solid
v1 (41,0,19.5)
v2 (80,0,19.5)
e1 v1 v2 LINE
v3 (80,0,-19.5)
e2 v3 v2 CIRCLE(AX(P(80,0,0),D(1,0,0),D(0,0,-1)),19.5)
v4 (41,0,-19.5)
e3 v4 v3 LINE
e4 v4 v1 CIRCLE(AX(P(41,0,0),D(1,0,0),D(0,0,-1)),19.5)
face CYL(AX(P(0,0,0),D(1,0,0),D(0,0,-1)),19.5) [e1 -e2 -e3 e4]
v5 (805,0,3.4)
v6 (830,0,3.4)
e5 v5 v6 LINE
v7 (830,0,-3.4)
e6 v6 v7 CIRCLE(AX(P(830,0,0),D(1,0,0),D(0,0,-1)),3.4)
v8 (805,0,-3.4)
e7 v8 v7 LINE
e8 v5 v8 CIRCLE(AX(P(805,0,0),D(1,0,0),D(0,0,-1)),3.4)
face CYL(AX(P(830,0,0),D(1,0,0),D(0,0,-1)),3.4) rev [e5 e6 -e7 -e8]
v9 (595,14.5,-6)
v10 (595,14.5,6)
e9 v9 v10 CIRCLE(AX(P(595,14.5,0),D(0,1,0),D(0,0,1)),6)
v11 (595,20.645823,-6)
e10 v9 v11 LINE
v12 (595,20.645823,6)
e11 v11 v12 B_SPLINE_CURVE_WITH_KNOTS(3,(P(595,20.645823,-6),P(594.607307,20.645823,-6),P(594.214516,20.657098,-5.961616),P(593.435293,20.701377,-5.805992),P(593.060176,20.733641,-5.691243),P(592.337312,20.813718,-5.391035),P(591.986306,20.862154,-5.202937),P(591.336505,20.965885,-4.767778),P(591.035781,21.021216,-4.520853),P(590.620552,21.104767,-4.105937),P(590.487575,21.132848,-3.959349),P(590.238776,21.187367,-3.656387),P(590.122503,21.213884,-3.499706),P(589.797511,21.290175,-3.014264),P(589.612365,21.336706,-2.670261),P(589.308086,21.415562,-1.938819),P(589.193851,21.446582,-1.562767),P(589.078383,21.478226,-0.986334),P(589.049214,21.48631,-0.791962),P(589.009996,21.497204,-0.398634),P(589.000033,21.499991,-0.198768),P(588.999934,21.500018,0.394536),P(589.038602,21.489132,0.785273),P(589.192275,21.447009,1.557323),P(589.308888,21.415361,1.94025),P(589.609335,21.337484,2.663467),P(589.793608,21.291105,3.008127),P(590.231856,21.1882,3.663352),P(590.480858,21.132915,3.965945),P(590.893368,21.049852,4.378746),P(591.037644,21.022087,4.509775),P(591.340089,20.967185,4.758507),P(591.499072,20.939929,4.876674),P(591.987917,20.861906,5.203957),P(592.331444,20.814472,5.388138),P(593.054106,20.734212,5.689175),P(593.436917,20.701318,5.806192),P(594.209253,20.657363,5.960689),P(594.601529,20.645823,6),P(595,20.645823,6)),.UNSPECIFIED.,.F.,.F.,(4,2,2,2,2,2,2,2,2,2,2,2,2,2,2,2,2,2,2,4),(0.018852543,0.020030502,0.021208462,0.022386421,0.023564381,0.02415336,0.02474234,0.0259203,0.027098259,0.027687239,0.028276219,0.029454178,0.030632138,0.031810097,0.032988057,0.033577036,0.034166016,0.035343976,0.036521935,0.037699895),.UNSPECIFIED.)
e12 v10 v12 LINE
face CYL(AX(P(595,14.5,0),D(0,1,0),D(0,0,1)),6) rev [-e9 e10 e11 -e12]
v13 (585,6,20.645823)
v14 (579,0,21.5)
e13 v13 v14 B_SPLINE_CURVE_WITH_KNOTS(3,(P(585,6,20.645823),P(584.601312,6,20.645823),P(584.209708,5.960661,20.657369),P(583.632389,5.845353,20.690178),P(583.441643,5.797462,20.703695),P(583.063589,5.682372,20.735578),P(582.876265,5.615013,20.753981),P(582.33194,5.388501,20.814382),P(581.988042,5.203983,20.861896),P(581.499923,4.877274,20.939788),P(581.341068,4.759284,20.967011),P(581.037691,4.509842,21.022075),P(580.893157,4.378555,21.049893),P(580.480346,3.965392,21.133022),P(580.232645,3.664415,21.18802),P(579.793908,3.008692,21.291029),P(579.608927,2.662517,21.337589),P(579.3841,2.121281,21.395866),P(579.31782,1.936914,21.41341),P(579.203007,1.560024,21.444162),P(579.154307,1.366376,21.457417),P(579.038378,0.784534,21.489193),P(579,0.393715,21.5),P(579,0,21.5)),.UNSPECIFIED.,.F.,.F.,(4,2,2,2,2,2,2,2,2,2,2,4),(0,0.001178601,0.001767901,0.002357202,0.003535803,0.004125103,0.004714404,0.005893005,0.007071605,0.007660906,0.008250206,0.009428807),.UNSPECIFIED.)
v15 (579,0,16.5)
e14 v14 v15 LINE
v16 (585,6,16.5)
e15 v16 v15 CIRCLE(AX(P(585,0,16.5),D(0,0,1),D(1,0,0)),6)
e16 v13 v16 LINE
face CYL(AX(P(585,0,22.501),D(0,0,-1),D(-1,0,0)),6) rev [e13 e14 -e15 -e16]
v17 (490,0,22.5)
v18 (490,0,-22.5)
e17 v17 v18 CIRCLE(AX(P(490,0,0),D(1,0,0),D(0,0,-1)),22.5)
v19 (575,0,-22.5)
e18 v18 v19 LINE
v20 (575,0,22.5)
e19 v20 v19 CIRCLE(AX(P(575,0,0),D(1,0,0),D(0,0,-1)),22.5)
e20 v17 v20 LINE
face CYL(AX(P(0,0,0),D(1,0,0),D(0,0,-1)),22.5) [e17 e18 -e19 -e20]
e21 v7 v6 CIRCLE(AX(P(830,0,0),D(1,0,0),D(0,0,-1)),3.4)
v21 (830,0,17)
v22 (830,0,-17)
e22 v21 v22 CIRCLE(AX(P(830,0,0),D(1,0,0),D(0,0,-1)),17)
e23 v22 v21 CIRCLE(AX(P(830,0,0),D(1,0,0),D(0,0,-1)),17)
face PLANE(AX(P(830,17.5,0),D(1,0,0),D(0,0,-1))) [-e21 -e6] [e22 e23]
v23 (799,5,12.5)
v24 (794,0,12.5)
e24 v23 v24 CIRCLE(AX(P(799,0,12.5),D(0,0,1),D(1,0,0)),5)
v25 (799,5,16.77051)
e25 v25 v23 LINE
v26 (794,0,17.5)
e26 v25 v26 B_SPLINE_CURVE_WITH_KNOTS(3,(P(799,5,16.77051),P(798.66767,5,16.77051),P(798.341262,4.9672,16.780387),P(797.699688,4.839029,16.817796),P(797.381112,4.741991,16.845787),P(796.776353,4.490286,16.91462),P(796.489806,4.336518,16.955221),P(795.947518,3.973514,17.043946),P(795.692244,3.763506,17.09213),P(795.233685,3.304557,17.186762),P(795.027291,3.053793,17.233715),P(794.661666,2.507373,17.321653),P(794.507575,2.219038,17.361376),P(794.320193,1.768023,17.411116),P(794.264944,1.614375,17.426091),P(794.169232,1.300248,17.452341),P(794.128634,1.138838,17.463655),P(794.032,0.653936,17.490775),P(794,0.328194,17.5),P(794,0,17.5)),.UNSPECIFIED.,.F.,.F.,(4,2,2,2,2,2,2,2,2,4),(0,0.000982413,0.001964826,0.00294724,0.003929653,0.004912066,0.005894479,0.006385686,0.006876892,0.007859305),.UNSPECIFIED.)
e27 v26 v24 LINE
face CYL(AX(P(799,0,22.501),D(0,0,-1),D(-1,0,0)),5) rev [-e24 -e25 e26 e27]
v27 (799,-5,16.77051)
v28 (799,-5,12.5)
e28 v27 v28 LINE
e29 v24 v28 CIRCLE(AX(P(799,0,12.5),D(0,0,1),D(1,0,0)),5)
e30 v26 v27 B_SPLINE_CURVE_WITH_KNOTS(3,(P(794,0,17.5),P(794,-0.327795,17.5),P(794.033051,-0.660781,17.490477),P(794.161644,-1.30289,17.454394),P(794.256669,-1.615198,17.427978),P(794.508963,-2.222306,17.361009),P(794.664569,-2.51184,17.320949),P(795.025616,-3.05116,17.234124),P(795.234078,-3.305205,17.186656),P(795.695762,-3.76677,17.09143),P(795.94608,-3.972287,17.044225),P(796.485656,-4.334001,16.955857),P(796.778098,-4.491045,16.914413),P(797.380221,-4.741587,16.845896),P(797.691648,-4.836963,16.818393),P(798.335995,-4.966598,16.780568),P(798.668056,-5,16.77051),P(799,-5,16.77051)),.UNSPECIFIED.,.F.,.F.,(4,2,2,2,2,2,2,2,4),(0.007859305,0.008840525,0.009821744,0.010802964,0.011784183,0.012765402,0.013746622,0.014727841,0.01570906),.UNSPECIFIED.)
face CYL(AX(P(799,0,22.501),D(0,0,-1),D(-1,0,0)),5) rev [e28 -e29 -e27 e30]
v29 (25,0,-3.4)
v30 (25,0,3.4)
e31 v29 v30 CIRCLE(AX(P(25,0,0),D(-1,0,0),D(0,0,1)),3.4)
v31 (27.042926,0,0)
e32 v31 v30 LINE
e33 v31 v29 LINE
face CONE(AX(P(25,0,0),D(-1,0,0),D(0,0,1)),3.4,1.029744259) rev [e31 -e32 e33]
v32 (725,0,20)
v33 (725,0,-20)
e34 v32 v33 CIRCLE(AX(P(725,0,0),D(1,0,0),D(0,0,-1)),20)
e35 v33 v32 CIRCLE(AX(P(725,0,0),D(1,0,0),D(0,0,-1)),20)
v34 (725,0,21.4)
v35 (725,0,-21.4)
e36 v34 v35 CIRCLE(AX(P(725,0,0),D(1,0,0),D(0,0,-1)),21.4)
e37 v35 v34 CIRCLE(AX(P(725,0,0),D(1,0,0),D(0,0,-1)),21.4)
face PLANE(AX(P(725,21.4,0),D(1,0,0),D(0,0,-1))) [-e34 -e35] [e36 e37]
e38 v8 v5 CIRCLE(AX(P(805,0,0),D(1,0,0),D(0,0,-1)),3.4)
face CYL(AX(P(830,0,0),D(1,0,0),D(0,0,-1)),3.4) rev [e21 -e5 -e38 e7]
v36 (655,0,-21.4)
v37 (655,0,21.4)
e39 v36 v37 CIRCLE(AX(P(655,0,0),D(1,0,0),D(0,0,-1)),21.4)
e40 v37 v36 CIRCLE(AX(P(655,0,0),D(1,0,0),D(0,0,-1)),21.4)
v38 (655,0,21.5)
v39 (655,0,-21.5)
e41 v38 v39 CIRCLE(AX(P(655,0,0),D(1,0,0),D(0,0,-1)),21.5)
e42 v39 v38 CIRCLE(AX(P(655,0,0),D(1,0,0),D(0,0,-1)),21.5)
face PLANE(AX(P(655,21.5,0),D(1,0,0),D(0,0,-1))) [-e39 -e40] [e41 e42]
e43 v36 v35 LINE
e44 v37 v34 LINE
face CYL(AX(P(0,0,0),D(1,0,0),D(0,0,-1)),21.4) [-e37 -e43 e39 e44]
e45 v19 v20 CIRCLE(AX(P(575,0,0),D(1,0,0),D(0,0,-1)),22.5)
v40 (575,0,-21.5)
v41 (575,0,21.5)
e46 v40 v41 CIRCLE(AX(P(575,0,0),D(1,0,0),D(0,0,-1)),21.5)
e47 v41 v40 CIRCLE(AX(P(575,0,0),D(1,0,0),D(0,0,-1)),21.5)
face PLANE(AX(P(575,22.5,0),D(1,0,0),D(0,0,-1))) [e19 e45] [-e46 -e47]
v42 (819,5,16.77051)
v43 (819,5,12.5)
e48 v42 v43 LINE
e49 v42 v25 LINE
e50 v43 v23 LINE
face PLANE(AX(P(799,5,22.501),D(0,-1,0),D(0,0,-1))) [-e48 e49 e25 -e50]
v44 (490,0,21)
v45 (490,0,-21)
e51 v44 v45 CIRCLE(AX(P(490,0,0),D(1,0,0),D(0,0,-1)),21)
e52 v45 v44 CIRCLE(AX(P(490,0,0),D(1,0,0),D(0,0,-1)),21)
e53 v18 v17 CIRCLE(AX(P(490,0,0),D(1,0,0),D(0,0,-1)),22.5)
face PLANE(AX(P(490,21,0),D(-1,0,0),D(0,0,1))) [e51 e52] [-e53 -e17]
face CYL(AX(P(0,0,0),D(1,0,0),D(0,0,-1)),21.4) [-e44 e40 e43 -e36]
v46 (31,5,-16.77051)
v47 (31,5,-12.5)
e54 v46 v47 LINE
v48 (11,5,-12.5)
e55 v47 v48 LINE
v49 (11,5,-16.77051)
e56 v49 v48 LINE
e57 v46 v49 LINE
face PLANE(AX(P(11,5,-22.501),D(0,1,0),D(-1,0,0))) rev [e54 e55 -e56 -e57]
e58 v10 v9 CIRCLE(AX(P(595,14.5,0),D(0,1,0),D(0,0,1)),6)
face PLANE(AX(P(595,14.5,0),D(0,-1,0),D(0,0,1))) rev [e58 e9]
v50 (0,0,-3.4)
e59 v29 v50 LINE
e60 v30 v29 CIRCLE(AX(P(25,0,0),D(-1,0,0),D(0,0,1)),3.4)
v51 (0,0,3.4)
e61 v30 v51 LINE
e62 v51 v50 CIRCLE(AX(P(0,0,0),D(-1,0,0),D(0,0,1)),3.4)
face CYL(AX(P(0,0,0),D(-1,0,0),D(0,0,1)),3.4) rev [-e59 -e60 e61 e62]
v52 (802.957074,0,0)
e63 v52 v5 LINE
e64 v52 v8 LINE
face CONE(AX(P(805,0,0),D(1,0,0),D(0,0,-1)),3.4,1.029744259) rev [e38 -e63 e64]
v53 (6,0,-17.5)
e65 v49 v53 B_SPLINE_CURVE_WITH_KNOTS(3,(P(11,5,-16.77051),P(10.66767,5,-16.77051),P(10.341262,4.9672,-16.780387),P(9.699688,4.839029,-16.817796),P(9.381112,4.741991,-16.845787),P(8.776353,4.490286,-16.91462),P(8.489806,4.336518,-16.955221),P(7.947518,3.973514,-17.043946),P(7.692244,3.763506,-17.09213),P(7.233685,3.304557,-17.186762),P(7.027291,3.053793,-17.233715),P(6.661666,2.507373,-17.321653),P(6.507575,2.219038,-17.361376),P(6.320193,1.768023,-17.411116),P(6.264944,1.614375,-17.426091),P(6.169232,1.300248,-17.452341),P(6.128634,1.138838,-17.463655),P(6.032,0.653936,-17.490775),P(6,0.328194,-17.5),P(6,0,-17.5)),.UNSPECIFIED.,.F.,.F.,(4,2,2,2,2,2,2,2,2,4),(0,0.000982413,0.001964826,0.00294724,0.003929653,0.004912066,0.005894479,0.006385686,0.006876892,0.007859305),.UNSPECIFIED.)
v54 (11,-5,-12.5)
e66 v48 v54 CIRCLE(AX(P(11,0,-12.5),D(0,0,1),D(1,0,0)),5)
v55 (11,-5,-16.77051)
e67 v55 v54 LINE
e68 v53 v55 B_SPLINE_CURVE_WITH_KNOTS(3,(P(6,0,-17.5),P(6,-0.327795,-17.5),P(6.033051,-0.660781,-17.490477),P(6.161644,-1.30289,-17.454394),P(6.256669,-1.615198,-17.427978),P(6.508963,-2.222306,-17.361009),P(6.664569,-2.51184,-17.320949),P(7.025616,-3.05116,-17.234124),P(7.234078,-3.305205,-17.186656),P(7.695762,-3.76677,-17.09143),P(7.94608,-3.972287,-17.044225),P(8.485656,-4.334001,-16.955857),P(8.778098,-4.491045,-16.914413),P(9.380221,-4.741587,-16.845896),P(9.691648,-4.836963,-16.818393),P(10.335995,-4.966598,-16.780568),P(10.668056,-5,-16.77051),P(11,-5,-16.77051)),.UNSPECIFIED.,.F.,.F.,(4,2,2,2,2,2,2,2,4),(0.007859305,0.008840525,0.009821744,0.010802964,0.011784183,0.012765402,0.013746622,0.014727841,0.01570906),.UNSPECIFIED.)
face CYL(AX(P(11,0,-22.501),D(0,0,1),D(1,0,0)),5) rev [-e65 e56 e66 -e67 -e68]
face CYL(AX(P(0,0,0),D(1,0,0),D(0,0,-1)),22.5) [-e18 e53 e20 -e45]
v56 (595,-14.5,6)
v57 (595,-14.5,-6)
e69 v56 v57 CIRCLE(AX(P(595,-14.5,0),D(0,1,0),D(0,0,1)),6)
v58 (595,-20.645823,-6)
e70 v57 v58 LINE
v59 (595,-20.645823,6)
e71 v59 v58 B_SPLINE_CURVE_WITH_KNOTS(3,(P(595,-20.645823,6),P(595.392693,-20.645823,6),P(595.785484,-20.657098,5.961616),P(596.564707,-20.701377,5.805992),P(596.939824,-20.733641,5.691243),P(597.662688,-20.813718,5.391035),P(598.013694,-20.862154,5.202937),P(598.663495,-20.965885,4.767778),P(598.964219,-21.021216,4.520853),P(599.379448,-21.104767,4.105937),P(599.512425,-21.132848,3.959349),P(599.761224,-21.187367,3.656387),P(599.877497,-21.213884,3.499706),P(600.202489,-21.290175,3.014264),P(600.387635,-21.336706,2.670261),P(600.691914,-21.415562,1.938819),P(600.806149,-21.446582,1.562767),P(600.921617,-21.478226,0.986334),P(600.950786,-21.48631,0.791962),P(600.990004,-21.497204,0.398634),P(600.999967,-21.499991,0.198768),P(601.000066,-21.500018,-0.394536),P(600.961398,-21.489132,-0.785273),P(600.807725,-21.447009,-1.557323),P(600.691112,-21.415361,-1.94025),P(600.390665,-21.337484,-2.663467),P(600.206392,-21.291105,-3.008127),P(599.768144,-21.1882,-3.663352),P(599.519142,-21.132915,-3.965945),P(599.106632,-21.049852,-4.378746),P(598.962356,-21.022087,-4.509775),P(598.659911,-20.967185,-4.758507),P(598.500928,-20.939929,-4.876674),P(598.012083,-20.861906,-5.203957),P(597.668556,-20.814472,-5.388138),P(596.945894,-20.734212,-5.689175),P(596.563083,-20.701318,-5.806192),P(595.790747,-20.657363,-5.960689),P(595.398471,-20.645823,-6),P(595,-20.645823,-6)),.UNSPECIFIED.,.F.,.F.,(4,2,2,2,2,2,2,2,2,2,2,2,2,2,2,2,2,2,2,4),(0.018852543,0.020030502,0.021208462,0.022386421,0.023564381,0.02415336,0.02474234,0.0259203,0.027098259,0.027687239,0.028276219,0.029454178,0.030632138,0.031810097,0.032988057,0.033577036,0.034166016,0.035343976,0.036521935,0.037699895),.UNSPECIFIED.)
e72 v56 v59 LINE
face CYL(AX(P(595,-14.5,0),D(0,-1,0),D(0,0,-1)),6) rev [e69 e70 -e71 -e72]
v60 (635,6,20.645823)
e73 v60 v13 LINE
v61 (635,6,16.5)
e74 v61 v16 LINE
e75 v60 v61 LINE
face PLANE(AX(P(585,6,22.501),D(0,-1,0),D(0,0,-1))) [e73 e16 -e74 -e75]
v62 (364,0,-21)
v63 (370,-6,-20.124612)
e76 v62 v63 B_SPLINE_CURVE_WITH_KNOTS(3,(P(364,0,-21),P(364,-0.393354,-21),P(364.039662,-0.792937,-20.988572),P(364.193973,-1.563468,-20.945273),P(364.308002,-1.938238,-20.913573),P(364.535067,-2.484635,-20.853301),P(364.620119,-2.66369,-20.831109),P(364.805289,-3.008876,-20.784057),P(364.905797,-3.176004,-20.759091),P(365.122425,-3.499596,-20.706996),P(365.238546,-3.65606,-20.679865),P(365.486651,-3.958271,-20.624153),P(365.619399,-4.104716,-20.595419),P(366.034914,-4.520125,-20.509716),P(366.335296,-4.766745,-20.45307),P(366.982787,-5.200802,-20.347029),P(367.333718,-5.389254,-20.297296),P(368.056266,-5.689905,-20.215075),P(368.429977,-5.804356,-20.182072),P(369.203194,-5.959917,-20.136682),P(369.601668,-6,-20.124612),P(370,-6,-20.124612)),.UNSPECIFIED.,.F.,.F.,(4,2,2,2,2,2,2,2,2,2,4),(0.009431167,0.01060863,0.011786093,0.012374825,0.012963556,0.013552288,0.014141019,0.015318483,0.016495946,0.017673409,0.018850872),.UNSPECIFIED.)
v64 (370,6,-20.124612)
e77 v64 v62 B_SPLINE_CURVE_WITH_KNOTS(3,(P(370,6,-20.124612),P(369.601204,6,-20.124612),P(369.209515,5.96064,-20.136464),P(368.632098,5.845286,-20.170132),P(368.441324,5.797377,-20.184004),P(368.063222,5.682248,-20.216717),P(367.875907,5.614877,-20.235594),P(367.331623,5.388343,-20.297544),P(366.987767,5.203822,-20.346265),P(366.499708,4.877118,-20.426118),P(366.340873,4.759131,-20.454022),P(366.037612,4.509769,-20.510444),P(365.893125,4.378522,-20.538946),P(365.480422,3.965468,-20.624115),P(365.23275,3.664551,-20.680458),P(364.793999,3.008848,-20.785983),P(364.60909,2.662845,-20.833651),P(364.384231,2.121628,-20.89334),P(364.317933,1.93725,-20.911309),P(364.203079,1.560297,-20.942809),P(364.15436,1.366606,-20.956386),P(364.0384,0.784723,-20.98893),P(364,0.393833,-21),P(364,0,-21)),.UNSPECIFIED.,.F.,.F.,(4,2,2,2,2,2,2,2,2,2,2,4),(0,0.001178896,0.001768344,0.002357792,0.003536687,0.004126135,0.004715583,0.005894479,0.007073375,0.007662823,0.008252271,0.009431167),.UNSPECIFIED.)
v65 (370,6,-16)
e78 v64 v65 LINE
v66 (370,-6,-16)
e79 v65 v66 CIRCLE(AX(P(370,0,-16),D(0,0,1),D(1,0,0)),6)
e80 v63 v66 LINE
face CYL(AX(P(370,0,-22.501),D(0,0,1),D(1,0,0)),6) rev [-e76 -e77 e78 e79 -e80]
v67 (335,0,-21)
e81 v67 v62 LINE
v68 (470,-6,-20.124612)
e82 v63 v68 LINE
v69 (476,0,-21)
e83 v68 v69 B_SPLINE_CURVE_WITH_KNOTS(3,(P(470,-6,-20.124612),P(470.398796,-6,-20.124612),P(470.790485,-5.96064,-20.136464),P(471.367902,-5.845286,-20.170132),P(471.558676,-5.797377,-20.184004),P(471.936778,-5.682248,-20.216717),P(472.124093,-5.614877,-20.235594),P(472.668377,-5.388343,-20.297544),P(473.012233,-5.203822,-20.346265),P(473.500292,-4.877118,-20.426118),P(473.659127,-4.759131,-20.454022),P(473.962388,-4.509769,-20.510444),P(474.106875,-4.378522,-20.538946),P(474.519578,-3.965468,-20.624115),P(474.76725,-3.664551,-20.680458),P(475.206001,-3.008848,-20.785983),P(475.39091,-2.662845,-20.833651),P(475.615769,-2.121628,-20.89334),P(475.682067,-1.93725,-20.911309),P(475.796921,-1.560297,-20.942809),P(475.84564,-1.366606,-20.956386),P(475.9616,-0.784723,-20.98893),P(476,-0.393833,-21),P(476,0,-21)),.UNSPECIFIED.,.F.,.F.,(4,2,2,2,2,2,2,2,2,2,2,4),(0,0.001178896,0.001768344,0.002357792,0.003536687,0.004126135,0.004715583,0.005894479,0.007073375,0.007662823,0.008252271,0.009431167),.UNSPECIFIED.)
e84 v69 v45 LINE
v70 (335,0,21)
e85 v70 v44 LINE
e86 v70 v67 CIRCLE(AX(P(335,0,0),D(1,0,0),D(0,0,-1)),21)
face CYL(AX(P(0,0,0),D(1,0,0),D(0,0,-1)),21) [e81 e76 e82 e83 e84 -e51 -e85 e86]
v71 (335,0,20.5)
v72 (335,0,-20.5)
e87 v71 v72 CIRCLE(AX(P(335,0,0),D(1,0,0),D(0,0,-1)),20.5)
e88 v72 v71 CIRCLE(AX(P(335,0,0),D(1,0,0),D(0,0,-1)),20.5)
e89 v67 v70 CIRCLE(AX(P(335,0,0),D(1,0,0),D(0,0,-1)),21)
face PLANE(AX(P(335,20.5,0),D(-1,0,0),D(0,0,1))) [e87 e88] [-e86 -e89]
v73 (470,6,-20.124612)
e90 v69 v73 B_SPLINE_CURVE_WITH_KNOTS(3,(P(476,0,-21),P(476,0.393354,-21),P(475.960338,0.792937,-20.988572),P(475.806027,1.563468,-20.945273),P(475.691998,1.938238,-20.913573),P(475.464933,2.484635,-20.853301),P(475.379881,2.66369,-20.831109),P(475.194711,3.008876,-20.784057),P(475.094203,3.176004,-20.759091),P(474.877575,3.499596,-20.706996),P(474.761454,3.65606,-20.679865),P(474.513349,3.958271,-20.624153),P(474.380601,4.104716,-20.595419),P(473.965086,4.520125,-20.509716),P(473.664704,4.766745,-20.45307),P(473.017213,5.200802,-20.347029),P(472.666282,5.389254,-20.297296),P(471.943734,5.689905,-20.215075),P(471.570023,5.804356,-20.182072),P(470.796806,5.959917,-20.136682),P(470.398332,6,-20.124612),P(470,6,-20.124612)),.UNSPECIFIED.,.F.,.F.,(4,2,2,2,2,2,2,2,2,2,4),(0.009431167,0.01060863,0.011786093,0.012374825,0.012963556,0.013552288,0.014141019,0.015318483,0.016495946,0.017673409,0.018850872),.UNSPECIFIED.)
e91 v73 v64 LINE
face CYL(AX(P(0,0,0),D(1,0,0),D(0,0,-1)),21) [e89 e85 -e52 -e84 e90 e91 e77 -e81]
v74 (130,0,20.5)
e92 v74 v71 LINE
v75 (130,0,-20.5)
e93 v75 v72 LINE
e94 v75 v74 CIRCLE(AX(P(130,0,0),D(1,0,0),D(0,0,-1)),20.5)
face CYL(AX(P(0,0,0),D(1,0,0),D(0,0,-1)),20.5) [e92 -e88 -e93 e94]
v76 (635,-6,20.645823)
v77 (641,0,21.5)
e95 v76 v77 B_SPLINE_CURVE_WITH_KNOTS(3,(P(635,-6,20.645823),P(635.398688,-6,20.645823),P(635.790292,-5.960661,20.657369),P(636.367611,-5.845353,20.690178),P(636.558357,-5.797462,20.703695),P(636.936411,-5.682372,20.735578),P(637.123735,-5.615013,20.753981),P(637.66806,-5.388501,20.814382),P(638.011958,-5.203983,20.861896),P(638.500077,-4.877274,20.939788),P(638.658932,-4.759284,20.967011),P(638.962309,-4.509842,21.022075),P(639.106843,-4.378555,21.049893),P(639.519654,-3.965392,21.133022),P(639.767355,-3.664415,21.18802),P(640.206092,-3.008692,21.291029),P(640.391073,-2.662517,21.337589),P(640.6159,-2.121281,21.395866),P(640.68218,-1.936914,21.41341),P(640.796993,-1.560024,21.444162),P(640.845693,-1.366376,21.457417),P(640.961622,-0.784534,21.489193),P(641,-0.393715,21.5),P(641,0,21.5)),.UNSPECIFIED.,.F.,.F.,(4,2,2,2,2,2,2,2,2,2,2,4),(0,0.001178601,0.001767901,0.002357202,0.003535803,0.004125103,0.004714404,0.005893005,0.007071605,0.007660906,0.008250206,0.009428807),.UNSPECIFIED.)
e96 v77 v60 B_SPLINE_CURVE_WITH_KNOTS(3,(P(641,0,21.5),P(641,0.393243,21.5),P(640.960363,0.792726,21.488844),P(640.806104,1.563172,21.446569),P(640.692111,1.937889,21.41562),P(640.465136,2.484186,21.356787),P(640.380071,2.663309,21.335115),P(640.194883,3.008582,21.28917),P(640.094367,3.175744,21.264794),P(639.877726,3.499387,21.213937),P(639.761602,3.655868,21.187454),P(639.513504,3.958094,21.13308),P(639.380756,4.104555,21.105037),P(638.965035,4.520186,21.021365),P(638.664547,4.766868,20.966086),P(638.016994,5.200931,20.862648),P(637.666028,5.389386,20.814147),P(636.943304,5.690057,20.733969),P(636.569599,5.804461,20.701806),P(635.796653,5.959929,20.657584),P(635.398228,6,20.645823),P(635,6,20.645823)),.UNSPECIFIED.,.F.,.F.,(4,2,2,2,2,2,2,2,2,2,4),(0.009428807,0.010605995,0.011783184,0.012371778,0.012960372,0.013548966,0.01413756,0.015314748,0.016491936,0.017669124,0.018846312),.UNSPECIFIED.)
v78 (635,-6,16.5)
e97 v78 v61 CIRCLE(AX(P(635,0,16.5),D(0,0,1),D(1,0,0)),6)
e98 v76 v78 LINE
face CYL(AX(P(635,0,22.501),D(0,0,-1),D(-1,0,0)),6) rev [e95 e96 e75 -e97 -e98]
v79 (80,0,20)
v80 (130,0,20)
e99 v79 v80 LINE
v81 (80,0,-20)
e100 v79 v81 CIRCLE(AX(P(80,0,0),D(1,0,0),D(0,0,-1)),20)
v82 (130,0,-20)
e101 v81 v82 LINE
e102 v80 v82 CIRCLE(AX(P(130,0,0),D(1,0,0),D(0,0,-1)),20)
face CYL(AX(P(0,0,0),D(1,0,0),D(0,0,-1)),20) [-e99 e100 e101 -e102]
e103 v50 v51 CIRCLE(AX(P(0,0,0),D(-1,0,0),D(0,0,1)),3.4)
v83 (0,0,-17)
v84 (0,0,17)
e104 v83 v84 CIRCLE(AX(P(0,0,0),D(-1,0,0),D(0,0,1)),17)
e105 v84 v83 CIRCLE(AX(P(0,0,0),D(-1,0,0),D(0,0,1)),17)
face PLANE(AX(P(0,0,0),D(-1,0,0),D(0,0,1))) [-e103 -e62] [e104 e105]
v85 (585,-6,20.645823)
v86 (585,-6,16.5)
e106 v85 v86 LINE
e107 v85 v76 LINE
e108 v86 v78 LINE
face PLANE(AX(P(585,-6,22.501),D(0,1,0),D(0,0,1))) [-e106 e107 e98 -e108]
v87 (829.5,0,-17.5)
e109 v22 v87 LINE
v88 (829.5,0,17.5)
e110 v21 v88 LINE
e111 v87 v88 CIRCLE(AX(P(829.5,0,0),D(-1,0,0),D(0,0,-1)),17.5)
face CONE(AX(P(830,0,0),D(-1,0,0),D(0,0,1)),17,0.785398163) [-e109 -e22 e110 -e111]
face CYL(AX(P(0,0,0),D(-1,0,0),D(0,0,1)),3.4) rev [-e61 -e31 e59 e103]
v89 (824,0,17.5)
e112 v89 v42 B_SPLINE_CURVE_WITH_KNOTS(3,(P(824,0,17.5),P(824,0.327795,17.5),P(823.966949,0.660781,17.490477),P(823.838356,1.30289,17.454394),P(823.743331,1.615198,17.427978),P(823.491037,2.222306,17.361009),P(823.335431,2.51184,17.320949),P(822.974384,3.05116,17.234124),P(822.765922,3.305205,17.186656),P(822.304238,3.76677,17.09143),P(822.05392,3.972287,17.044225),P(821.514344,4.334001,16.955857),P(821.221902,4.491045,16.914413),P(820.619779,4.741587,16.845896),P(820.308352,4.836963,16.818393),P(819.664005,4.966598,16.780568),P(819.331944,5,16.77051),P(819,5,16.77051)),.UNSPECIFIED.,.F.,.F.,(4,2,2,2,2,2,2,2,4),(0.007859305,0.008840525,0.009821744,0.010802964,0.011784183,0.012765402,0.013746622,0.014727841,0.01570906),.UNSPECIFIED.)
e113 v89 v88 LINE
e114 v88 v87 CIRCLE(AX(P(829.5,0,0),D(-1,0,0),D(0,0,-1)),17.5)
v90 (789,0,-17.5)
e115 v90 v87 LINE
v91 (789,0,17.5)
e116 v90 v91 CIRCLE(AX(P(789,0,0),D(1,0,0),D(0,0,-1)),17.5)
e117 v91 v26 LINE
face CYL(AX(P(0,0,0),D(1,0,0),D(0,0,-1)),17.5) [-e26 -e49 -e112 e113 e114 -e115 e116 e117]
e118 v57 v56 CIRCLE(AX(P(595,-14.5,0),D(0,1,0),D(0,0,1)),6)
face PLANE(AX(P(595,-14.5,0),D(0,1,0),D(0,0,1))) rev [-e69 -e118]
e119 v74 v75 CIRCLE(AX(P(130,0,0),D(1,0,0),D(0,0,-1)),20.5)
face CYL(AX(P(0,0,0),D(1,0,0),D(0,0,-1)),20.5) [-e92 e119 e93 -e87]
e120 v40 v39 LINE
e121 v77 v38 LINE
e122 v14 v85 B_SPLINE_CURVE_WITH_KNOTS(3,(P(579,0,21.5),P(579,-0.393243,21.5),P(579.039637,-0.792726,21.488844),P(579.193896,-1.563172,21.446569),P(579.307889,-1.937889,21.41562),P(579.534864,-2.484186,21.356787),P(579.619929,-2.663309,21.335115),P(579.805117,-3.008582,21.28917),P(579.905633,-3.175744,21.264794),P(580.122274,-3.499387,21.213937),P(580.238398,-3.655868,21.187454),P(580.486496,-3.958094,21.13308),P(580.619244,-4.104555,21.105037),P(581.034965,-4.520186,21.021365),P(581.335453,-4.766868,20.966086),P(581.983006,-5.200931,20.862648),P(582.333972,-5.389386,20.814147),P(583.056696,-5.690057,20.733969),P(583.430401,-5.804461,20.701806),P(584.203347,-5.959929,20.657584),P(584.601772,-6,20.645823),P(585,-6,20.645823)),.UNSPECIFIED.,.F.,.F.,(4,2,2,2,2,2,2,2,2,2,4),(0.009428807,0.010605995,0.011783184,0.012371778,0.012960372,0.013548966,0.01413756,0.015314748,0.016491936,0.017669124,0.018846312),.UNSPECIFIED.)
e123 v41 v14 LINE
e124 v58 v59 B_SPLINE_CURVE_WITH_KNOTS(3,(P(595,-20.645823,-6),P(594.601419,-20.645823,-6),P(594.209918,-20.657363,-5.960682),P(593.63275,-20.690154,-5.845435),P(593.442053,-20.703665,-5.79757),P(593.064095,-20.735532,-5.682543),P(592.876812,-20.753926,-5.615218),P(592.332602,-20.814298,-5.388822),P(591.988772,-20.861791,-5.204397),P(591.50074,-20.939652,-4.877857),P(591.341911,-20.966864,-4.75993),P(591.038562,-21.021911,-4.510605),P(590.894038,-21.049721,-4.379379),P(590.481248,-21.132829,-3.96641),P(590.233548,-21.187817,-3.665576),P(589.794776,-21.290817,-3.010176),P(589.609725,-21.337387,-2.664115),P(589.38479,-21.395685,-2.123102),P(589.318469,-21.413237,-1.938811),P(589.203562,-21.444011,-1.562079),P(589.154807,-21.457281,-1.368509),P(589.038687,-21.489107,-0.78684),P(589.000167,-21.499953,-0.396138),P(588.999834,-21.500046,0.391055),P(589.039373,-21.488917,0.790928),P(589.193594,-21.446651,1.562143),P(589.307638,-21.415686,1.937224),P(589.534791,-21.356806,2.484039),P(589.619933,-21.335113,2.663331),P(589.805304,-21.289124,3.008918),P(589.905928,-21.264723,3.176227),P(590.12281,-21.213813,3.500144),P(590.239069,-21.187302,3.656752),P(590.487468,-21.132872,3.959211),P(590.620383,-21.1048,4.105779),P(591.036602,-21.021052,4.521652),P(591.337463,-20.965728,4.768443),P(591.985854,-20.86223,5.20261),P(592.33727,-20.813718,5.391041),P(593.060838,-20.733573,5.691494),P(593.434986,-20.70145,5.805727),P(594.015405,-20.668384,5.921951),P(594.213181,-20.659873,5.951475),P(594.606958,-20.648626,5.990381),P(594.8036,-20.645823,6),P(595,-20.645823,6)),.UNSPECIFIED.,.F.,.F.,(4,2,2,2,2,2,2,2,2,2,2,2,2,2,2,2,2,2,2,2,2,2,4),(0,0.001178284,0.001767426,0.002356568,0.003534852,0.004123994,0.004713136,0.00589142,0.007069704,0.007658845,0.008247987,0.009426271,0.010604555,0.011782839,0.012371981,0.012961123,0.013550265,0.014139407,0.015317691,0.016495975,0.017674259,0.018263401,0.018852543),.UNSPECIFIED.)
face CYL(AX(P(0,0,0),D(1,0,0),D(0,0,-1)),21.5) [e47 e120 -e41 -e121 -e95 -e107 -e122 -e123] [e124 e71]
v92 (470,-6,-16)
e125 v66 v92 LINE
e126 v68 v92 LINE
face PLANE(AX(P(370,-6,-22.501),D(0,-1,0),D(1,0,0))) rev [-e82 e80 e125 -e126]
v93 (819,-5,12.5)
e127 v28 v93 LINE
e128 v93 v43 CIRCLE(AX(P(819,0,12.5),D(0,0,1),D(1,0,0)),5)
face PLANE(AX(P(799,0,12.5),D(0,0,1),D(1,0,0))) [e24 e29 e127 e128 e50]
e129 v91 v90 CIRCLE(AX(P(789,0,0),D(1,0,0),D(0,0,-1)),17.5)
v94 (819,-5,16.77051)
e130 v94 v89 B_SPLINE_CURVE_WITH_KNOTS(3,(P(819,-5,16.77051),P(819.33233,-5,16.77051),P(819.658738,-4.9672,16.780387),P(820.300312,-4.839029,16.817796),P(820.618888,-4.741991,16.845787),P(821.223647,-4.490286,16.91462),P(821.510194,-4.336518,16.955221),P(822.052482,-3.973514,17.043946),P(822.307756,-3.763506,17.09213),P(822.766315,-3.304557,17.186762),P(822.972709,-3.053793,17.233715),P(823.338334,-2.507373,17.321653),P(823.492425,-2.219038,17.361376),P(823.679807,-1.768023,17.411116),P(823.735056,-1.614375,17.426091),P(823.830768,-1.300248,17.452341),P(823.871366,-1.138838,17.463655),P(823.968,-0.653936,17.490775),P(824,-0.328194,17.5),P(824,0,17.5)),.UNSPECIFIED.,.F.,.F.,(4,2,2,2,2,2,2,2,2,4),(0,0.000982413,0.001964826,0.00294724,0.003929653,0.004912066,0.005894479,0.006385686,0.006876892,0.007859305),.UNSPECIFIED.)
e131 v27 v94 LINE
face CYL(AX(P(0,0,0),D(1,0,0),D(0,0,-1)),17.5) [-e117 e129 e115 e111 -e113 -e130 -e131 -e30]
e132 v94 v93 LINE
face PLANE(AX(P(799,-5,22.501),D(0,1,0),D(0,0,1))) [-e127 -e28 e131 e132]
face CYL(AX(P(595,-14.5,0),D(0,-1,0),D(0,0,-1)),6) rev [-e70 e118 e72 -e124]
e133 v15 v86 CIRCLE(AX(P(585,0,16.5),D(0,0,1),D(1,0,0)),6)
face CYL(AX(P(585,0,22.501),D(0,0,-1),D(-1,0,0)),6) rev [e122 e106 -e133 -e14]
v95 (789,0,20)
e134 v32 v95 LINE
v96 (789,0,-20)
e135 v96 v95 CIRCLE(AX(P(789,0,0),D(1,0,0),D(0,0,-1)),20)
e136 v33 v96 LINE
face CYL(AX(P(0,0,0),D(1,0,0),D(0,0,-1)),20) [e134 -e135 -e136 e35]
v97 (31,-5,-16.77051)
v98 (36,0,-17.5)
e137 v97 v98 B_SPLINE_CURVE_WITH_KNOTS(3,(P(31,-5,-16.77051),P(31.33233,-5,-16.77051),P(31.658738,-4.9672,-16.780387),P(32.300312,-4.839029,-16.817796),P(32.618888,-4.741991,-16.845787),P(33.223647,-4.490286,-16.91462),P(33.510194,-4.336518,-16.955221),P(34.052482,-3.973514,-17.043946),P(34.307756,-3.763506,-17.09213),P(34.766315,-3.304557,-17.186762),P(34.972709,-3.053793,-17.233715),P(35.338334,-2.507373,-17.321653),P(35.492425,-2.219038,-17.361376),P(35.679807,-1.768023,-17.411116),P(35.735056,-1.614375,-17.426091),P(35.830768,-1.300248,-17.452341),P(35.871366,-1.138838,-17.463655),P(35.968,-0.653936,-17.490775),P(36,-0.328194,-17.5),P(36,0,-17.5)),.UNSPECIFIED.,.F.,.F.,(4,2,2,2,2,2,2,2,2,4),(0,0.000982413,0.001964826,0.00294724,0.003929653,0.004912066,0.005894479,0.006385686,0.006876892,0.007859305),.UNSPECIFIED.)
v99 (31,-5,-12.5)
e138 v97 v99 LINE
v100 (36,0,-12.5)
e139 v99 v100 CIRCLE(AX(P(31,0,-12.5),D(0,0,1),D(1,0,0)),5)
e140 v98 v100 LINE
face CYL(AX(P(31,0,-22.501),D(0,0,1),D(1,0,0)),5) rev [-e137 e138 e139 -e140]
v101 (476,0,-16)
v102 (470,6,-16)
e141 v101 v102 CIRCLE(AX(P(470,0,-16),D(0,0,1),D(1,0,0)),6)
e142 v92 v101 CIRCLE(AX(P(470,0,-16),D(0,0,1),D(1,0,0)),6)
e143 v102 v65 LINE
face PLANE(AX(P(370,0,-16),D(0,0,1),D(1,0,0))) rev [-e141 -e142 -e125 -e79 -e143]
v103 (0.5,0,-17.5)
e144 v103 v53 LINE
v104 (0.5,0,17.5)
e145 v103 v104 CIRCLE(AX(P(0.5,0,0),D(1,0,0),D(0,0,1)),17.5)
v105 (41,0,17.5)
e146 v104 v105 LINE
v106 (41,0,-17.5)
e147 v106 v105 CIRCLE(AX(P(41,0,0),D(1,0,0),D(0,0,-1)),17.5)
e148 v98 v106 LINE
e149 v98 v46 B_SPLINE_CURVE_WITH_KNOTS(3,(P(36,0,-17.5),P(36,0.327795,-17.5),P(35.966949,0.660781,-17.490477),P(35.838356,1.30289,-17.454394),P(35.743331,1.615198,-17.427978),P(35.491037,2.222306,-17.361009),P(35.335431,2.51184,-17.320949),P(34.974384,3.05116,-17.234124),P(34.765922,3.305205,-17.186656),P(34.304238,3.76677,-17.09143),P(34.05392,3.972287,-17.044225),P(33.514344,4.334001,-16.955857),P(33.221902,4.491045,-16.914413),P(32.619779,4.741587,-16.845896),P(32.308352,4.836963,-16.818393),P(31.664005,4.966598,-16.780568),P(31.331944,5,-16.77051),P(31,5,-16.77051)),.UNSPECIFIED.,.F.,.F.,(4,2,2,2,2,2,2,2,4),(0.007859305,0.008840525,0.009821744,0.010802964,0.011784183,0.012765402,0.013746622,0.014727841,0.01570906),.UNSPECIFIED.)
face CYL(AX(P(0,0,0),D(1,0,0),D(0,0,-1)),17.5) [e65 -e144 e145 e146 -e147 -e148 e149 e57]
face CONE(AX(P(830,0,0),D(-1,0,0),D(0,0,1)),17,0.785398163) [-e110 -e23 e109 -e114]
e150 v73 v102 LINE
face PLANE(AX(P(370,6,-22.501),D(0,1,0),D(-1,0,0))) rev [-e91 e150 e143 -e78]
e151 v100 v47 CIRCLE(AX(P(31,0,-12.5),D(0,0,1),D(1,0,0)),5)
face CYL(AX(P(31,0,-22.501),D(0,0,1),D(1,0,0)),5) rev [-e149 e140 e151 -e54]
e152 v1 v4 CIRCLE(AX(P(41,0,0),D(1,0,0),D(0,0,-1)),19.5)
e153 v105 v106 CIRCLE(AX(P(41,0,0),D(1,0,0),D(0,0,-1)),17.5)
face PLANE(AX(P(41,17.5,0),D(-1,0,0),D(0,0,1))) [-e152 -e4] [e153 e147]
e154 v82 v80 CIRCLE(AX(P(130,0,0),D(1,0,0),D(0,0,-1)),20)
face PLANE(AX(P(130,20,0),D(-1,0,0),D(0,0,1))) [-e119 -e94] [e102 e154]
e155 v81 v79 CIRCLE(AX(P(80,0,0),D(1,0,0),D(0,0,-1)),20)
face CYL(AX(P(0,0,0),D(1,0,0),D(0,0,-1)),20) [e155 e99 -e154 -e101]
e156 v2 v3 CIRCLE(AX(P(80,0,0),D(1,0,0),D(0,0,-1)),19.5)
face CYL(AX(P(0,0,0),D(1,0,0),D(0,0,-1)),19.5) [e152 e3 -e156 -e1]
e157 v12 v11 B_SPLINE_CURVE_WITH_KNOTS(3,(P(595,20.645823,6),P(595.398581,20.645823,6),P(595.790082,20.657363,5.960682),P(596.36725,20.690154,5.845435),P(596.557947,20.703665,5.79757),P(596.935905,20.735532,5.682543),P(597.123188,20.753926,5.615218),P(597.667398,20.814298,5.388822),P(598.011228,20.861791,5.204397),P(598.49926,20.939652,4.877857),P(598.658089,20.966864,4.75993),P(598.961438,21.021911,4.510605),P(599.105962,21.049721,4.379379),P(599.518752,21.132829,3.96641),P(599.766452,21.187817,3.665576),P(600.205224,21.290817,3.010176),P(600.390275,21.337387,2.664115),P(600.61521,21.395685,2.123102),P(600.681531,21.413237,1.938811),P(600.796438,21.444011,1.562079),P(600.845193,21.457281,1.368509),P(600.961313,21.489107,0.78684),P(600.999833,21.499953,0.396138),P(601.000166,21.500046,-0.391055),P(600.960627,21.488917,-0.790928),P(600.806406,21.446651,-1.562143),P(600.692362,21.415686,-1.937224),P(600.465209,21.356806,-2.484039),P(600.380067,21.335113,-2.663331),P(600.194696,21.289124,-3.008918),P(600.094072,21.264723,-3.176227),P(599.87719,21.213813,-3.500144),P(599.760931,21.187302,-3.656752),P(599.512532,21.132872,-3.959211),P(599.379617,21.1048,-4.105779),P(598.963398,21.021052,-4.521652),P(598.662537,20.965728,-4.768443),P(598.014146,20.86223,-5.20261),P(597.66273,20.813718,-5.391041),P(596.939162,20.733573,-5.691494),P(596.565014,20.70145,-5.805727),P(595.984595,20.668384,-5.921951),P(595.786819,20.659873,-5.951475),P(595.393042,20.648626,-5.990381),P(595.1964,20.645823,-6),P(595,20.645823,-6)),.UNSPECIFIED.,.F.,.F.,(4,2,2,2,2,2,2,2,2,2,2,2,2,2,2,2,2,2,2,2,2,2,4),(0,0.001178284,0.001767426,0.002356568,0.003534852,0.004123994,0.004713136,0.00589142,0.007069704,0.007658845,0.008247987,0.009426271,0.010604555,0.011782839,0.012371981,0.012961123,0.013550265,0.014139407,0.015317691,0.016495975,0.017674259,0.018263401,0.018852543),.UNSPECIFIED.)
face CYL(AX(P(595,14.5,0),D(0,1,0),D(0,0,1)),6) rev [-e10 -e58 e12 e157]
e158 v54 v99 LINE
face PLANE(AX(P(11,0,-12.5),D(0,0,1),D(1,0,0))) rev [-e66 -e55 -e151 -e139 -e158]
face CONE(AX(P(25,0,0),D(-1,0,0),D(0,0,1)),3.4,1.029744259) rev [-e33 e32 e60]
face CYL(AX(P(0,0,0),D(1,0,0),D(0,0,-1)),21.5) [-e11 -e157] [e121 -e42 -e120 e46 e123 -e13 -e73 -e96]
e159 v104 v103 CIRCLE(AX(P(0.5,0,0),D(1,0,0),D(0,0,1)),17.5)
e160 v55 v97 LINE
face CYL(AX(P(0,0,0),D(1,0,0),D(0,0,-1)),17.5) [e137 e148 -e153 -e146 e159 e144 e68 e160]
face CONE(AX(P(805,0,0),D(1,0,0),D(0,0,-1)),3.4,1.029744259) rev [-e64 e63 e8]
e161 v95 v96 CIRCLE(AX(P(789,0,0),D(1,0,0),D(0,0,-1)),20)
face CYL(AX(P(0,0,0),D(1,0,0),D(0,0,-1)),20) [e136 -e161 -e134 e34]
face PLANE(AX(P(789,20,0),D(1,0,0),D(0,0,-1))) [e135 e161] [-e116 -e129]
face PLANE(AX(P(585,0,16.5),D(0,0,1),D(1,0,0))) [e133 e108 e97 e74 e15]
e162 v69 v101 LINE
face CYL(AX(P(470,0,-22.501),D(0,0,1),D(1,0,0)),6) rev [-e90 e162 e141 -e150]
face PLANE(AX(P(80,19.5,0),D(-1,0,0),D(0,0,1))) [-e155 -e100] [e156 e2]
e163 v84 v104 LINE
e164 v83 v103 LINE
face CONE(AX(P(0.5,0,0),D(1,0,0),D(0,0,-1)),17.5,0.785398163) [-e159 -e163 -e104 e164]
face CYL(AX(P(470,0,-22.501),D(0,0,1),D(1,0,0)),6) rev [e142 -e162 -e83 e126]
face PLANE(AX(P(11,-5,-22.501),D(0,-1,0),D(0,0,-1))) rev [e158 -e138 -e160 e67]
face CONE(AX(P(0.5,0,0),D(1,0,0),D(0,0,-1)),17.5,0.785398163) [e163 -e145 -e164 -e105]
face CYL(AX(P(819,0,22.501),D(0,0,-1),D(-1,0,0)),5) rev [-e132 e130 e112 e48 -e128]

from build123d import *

# Parameters (mm, degrees)
M8_TAPPED_HOLE1_D       = 6.8
M8_TAPPED_HOLE1_DEPTH   = 25
M8_TAPPED_HOLE1_TIP     = 2.042926105
M8_TAPPED_HOLE2_D       = 6.8
M8_TAPPED_HOLE2_DEPTH   = 25
M8_TAPPED_HOLE2_TIP     = 2.042926105
CUT_EXTRUDE1_REACH      = 833.042
CUT_EXTRUDE1_END_RADIUS = 17.5
CUT_EXTRUDE2_REACH      = 833.197
CUT_EXTRUDE2_END_RADIUS = 21
CUT_EXTRUDE3_REACH      = 833.22
CUT_EXTRUDE3_END_RADIUS = 21.5
CUT_EXTRUDE4_REACH      = 833.042
CUT_EXTRUDE4_END_RADIUS = 17.5
CUT_EXTRUDE5_START      = -21.5
SKETCH11_R              = 6
CUT_EXTRUDE5_DEPTH      = 7
CHAMFER1_SIZE           = 0.5


with BuildPart() as part:
    # Sketch1 → Revolve1 (revolve)
    with BuildSketch(Plane.XY, mode=Mode.PRIVATE) as revolve1_sk:
        Polygon((0, 0), (0, 17.5), (41, 17.5), (41, 19.5), (80, 19.5), (80, 20), (130, 20), (130, 20.5), (335, 20.5), (335, 21), (490, 21), (490, 22.5), (575, 22.5), (575, 21.5), (655, 21.5), (655, 21.4), (725, 21.4), (725, 20), (789, 20), (789, 17.5), (830, 17.5), (830, 0), align=None)
    revolve(revolve1_sk.sketch.rotate(Axis((0, 0, 0), (-1, 0, 0)), 90), axis=Axis((0, 0, 0), (-1, 0, 0)))

    # M8 Tapped Hole1
    with Locations(Plane.ZY):
        with Locations((0, 0)):
            Hole(M8_TAPPED_HOLE1_D / 2, depth=M8_TAPPED_HOLE1_DEPTH)
            with Locations((0, 0, -(M8_TAPPED_HOLE1_DEPTH + M8_TAPPED_HOLE1_TIP / 2))):  # 118° drill point
                Cone(0, M8_TAPPED_HOLE1_D / 2, M8_TAPPED_HOLE1_TIP, mode=Mode.SUBTRACT)

    # M8 Tapped Hole2
    with Locations(Plane(origin=(830, 0, 0), x_dir=(0, 0, -1), z_dir=(1, 0, 0))):
        with Locations((0, 0)):
            Hole(M8_TAPPED_HOLE2_D / 2, depth=M8_TAPPED_HOLE2_DEPTH)
            with Locations((0, 0, -(M8_TAPPED_HOLE2_DEPTH + M8_TAPPED_HOLE2_TIP / 2))):  # 118° drill point
                Cone(0, M8_TAPPED_HOLE2_D / 2, M8_TAPPED_HOLE2_TIP, mode=Mode.SUBTRACT)

    # Cut-Extrude1: up to this cylinder (the profile starts inside it)
    cut_extrude1_end = Plane(origin=(21, 0, 0), z_dir=(1, 0, 0)) * Cylinder(CUT_EXTRUDE1_END_RADIUS, 1702.084, mode=Mode.PRIVATE)
    # Sketch6 → Cut-Extrude1 (cut, up to the surface)
    with BuildSketch(Plane.XY.offset(-12.5), mode=Mode.PRIVATE) as cut_extrude1_sk1:
        with BuildLine():
            Line((11, 5), (31, 5))
            ThreePointArc((31, 5), (36, 0), (31, -5))
            Line((31, -5), (11, -5))
            ThreePointArc((11, -5), (6, 0), (11, 5))
        make_face()
    cut_extrude1_tool1 = extrude(cut_extrude1_sk1.sketch, amount=-CUT_EXTRUDE1_REACH, mode=Mode.PRIVATE) & cut_extrude1_end
    add(cut_extrude1_tool1.solids().sort_by_distance((21, 0, -12.5))[0], mode=Mode.SUBTRACT)

    # Cut-Extrude2: up to this cylinder (the profile starts inside it)
    cut_extrude2_end = Plane(origin=(420, 0, 0), z_dir=(1, 0, 0)) * Cylinder(CUT_EXTRUDE2_END_RADIUS, 1709.394, mode=Mode.PRIVATE)
    # Sketch7 → Cut-Extrude2 (cut, up to the surface)
    with BuildSketch(Plane.XY.offset(-16), mode=Mode.PRIVATE) as cut_extrude2_sk1:
        with BuildLine():
            Line((370, 6), (470, 6))
            ThreePointArc((470, 6), (476, 0), (470, -6))
            Line((470, -6), (370, -6))
            ThreePointArc((370, -6), (364, 0), (370, 6))
        make_face()
    cut_extrude2_tool1 = extrude(cut_extrude2_sk1.sketch, amount=-CUT_EXTRUDE2_REACH, mode=Mode.PRIVATE) & cut_extrude2_end
    add(cut_extrude2_tool1.solids().sort_by_distance((420, 0, -16))[0], mode=Mode.SUBTRACT)

    # Cut-Extrude3: up to this cylinder (the profile starts inside it)
    cut_extrude3_end = Plane(origin=(610, 0, 0), z_dir=(1, 0, 0)) * Cylinder(CUT_EXTRUDE3_END_RADIUS, 1710.44, mode=Mode.PRIVATE)
    # Sketch9 → Cut-Extrude3 (cut, up to the surface)
    with BuildSketch(Plane.XY.offset(16.5), mode=Mode.PRIVATE) as cut_extrude3_sk1:
        with BuildLine():
            Line((585, 6), (635, 6))
            ThreePointArc((635, 6), (641, 0), (635, -6))
            Line((635, -6), (585, -6))
            ThreePointArc((585, -6), (579, 0), (585, 6))
        make_face()
    cut_extrude3_tool1 = extrude(cut_extrude3_sk1.sketch, amount=CUT_EXTRUDE3_REACH, mode=Mode.PRIVATE) & cut_extrude3_end
    add(cut_extrude3_tool1.solids().sort_by_distance((610, 0, 16.5))[0], mode=Mode.SUBTRACT)

    # Cut-Extrude4: up to this cylinder (the profile starts inside it)
    cut_extrude4_end = Plane(origin=(809, 0, 0), z_dir=(1, 0, 0)) * Cylinder(CUT_EXTRUDE4_END_RADIUS, 1702.084, mode=Mode.PRIVATE)
    # Sketch10 → Cut-Extrude4 (cut, up to the surface)
    with BuildSketch(Plane.XY.offset(12.5), mode=Mode.PRIVATE) as cut_extrude4_sk1:
        with BuildLine():
            Line((799, 5), (819, 5))
            ThreePointArc((819, 5), (824, 0), (819, -5))
            Line((819, -5), (799, -5))
            ThreePointArc((799, -5), (794, 0), (799, 5))
        make_face()
    cut_extrude4_tool1 = extrude(cut_extrude4_sk1.sketch, amount=CUT_EXTRUDE4_REACH, mode=Mode.PRIVATE) & cut_extrude4_end
    add(cut_extrude4_tool1.solids().sort_by_distance((809, 0, 12.5))[0], mode=Mode.SUBTRACT)

    # Sketch11 → Cut-Extrude5 (cut)
    with BuildSketch(Plane(origin=(0, 0, 0), x_dir=(1, 0, 0), z_dir=(0, 1, 0)).offset(CUT_EXTRUDE5_START)):
        with Locations(Location((595, 0, 0), (0, 0, 90))):
            Circle(SKETCH11_R)
    cut_extrude5 = extrude(amount=CUT_EXTRUDE5_DEPTH, mode=Mode.SUBTRACT)

    # Mirror1: Cut-Extrude5 across plane
    add(cut_extrude5.mirror(Plane.ZX), mode=Mode.SUBTRACT)

    # Chamfer1
    chamfer1_edges = [part.edges().sort_by_distance(p)[0] for p in [
        (830, 0, 17.5),
        (0, 0, 17.5),
    ]]
    chamfer(chamfer1_edges, length=CHAMFER1_SIZE)


solid = part.part
